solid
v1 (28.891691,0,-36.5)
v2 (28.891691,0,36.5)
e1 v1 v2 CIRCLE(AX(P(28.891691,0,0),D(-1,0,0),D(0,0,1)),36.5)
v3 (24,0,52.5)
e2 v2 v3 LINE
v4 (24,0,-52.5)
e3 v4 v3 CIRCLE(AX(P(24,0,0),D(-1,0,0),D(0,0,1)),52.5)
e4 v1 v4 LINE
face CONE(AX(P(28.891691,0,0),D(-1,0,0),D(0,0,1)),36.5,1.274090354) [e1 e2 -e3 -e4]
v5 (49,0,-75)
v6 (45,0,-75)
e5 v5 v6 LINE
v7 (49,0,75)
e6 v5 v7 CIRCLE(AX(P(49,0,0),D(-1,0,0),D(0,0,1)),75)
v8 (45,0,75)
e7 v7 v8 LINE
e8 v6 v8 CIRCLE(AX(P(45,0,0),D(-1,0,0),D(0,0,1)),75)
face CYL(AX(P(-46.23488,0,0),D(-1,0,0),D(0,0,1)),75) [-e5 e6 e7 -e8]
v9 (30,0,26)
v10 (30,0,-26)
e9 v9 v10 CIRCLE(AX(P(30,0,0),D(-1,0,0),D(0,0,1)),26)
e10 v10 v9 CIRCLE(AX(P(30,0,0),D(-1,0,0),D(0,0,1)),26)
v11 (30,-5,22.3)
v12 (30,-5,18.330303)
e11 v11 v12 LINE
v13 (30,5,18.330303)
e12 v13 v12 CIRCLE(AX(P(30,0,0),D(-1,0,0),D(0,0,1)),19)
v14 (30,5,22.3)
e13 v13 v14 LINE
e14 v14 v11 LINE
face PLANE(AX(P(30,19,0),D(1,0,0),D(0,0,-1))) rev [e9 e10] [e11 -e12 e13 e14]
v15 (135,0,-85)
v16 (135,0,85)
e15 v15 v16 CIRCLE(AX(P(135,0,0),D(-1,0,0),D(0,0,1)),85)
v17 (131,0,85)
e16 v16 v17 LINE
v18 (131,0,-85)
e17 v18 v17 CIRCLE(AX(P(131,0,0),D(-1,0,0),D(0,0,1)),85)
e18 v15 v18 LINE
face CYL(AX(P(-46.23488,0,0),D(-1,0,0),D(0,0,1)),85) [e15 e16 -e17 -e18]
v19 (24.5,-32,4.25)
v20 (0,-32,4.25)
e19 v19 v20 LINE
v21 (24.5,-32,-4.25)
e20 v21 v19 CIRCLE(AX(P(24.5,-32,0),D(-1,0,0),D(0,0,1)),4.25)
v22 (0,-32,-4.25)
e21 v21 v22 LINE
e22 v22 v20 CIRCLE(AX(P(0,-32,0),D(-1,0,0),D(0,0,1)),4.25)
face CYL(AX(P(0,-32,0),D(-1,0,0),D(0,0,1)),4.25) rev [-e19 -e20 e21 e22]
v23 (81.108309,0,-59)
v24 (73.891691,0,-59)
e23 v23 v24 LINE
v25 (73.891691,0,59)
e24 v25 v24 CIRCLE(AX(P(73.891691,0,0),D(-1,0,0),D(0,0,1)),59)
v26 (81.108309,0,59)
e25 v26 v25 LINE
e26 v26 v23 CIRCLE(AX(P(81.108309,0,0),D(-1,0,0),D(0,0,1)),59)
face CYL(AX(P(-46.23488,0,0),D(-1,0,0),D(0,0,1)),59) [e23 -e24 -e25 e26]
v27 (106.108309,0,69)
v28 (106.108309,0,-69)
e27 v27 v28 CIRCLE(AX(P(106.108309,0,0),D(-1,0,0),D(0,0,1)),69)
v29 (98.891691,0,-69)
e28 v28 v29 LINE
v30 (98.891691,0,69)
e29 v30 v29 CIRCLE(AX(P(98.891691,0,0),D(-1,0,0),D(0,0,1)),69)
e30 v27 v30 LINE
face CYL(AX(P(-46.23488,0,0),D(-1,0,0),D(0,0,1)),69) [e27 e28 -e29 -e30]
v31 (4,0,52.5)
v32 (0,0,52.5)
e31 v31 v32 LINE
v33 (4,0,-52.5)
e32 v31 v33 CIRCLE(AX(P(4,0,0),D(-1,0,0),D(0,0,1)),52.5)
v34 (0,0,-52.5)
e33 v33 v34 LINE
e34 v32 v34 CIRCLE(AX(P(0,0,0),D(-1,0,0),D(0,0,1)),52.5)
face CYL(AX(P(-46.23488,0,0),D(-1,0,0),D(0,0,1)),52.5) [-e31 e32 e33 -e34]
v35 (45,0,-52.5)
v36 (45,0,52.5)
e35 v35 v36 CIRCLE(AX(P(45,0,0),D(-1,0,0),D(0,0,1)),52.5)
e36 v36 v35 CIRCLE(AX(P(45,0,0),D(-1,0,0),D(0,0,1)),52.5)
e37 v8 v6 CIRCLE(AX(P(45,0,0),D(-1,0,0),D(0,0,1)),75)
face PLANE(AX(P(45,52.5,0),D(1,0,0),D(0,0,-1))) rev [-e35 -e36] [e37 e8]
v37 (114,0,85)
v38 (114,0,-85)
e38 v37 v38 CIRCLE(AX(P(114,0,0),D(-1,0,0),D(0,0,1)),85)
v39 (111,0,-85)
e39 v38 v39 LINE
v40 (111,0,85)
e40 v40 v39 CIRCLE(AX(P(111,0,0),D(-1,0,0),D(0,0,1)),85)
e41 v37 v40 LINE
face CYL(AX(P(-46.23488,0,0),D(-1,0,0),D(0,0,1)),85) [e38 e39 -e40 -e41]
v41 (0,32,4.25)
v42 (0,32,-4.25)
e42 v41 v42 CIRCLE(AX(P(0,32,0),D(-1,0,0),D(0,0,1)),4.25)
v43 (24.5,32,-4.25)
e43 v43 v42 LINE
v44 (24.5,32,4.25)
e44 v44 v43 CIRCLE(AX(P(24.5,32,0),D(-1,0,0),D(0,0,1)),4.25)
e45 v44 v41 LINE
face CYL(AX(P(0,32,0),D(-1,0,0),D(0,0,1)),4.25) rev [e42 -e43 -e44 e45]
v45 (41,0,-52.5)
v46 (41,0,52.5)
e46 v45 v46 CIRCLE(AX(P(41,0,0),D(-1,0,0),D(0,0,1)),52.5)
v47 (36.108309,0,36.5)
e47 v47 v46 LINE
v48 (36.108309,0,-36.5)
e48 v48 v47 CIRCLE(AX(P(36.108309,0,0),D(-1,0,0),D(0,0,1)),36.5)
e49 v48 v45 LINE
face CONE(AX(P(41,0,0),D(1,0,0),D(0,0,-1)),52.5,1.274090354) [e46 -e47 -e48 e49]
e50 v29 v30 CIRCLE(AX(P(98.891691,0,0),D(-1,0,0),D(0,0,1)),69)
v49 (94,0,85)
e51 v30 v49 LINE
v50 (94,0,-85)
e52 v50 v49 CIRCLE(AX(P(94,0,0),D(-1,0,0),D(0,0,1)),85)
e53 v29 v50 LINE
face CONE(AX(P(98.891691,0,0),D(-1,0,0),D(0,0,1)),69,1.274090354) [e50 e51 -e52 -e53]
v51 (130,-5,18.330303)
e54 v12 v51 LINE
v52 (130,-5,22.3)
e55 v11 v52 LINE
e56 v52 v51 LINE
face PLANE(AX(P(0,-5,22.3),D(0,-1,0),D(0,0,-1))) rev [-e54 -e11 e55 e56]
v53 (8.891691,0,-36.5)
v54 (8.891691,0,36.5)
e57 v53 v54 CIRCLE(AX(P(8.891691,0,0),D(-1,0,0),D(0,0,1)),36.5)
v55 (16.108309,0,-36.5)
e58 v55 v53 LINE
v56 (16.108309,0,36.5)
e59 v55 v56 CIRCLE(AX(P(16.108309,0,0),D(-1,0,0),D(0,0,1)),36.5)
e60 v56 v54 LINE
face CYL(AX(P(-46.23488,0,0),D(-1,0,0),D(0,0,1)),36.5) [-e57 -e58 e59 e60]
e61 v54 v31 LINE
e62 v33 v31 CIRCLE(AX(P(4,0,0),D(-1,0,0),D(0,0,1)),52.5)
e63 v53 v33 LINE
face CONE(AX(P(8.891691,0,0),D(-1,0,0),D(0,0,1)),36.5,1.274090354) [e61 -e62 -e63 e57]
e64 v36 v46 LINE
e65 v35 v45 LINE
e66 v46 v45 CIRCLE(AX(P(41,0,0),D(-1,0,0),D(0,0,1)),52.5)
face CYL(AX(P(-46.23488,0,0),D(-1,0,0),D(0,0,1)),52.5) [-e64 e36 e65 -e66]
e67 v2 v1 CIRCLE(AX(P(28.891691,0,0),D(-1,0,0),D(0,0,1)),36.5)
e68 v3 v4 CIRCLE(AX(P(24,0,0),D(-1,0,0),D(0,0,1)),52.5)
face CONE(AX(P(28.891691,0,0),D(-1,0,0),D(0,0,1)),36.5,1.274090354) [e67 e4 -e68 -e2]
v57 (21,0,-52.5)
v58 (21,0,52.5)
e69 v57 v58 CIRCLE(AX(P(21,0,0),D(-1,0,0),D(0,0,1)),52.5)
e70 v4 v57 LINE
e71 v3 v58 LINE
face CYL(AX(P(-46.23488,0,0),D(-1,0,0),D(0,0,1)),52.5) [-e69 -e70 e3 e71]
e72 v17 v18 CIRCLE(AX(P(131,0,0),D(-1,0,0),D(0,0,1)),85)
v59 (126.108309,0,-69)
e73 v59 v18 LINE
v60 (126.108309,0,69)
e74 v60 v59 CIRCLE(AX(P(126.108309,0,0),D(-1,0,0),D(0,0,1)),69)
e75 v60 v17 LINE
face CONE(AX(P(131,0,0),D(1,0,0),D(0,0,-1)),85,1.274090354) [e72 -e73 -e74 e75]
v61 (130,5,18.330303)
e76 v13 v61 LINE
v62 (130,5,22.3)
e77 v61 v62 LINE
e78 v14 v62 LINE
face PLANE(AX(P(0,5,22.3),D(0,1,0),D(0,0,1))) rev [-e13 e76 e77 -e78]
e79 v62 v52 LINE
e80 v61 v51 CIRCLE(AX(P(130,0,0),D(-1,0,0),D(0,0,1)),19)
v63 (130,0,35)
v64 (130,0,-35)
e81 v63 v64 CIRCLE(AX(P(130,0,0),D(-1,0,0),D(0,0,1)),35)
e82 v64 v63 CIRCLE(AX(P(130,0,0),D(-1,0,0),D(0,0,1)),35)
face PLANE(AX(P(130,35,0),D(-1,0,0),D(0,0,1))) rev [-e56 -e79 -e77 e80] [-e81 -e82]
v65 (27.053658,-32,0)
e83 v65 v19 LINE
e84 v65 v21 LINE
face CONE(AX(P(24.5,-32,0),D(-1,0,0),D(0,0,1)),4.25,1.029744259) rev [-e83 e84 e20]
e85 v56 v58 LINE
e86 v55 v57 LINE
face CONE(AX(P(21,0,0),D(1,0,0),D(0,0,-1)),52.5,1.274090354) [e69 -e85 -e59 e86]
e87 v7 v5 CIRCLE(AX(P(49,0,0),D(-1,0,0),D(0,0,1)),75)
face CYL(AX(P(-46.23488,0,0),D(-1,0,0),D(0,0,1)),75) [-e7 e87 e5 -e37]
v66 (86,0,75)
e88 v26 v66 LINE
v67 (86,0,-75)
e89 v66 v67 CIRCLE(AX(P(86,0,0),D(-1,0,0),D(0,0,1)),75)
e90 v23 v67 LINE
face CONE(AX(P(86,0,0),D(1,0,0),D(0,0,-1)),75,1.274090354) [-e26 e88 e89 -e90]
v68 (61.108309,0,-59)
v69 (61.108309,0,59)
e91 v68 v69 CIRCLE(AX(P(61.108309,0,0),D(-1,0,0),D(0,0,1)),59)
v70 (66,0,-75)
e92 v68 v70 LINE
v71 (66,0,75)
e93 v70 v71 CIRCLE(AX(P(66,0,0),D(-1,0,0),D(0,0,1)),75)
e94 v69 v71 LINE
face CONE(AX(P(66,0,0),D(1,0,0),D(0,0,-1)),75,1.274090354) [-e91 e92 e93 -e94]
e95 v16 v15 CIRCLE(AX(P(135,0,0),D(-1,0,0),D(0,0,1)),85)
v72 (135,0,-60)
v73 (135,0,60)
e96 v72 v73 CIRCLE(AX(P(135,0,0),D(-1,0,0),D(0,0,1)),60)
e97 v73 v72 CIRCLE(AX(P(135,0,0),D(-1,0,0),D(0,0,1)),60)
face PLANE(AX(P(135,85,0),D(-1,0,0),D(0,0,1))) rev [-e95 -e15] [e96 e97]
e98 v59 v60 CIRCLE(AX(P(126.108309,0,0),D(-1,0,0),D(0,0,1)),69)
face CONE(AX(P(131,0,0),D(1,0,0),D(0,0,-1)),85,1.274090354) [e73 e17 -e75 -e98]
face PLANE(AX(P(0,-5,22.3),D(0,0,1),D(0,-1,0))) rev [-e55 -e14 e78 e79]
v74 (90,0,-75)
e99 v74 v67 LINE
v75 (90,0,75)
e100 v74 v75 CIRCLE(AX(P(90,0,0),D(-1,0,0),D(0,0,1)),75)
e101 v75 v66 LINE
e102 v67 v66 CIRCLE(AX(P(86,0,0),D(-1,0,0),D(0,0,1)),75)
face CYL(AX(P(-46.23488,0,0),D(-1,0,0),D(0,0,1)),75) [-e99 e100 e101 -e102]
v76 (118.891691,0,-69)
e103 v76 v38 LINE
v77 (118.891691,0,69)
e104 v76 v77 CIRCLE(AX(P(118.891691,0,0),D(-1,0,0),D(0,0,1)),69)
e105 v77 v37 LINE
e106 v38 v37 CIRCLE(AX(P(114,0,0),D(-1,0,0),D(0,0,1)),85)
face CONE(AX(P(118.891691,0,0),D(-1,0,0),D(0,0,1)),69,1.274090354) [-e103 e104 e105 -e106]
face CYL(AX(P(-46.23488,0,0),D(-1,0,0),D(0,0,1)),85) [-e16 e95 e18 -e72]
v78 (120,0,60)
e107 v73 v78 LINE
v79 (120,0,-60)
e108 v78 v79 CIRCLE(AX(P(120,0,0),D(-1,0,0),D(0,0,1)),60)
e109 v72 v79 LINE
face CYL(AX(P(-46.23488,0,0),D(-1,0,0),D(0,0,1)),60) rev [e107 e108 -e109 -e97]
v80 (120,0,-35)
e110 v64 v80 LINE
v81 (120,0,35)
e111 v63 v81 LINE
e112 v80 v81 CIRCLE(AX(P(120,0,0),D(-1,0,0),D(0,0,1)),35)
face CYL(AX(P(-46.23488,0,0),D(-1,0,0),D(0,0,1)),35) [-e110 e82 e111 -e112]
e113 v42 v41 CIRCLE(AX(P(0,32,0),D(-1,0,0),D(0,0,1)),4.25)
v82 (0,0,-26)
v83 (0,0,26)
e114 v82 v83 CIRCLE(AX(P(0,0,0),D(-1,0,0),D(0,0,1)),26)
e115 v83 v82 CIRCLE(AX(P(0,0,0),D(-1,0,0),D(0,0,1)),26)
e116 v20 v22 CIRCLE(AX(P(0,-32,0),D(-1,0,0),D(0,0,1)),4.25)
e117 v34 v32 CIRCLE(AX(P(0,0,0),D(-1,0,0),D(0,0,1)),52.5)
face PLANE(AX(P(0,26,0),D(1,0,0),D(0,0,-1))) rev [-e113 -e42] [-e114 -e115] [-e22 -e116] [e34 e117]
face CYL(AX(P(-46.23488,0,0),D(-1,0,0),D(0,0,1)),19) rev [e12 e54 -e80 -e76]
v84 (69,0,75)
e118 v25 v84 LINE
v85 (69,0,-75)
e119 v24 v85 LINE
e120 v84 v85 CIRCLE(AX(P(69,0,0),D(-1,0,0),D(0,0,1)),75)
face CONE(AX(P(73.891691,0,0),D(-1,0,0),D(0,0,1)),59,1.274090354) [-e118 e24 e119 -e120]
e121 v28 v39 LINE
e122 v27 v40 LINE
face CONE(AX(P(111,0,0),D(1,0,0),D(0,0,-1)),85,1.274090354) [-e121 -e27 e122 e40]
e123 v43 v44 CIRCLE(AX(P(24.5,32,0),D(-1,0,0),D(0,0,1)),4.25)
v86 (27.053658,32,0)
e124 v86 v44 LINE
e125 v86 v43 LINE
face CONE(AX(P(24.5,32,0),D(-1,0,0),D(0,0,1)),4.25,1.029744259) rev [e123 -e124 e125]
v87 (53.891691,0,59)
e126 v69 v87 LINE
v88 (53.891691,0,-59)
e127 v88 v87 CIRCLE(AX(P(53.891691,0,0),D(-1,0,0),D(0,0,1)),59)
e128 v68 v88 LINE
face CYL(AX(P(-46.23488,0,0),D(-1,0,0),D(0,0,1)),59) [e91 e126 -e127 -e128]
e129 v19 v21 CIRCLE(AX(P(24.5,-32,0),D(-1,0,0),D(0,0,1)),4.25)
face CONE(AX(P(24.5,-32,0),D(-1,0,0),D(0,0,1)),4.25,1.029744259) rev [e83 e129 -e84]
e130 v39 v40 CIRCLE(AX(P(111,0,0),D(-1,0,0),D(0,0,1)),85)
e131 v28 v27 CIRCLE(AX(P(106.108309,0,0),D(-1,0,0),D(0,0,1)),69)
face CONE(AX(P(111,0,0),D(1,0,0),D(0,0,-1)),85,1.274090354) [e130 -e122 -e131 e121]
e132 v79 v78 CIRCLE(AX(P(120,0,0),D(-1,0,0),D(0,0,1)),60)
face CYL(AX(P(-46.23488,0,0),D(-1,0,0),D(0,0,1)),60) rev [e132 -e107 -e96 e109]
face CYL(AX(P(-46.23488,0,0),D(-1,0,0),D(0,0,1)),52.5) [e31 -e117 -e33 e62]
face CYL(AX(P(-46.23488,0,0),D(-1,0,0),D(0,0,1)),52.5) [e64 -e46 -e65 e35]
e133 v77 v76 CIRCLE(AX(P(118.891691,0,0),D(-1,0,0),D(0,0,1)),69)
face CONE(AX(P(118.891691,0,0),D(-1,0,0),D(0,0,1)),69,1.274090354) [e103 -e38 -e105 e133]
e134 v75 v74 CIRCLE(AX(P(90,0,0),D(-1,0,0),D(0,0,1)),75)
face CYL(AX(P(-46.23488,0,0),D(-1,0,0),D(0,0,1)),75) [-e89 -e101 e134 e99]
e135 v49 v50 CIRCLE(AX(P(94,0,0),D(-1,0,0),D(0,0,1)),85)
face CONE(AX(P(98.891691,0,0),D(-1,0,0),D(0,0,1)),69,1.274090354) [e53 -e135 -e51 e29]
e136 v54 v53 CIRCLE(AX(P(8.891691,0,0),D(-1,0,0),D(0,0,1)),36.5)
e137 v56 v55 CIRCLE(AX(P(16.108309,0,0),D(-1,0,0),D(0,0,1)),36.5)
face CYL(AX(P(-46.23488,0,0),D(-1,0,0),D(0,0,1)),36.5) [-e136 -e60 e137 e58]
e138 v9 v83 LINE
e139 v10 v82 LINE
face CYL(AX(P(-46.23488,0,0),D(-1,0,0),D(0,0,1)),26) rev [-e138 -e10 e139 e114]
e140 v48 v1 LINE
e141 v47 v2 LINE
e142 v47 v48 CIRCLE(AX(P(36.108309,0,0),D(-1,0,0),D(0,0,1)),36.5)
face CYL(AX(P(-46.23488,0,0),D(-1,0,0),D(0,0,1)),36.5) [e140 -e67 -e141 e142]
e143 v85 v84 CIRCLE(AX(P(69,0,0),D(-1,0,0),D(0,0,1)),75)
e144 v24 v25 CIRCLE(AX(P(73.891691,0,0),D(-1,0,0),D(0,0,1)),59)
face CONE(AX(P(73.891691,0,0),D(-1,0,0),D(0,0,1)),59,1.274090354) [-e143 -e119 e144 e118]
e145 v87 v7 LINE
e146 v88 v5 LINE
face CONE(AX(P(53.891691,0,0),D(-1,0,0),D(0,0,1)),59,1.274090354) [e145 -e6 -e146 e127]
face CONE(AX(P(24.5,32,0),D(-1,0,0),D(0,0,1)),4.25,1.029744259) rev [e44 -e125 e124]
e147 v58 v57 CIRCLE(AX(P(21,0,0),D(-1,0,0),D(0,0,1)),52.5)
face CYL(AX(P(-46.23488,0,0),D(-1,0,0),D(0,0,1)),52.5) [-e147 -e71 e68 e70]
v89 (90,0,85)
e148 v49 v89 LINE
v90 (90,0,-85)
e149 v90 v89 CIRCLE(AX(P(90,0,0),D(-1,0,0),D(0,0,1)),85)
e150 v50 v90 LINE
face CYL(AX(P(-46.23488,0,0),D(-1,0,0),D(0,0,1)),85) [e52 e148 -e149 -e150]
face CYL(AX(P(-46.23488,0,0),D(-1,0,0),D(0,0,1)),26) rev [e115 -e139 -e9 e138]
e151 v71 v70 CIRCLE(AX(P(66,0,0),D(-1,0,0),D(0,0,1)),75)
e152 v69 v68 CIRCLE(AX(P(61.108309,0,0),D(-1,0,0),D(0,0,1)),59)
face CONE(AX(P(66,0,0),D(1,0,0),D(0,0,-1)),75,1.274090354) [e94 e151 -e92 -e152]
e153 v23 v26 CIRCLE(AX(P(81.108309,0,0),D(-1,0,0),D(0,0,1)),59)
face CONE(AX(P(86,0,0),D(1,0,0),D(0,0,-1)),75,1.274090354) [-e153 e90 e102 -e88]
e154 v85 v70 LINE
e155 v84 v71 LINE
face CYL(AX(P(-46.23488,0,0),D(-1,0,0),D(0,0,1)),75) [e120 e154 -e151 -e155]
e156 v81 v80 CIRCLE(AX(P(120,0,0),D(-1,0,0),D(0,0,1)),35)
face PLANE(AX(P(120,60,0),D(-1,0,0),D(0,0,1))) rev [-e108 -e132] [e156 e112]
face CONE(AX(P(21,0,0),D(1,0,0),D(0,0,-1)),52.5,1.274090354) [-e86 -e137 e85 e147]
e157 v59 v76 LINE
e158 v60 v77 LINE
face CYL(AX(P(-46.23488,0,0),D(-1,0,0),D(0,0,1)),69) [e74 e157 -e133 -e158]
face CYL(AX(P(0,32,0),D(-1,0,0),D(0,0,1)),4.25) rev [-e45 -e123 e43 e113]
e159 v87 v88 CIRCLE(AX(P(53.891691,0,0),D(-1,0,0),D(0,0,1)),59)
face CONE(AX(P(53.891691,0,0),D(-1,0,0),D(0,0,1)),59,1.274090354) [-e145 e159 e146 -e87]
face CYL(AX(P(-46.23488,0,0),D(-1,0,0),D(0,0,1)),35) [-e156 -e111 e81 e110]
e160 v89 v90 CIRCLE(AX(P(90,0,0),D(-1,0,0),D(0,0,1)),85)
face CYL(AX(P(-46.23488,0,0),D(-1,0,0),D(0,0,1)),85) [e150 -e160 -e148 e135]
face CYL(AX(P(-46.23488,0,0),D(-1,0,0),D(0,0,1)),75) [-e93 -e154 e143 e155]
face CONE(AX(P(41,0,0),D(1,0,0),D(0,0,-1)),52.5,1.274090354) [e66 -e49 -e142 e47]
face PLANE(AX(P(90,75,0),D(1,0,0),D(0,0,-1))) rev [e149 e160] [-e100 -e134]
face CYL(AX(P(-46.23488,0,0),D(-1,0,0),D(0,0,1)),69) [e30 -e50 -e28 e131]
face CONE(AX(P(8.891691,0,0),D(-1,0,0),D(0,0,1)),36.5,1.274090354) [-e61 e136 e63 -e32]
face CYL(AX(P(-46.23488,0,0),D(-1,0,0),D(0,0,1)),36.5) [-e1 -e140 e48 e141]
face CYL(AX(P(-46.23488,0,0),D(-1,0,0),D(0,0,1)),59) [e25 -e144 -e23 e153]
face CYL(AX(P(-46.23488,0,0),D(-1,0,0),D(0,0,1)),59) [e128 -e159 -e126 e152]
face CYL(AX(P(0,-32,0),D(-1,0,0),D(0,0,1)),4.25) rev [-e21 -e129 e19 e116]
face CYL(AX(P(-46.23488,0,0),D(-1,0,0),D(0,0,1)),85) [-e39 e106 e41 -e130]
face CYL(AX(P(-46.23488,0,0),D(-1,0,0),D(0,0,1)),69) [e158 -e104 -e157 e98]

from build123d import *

# Parameters (mm, degrees)
HOLE_WIZARD_M10_1_D     = 8.5
HOLE_WIZARD_M10_1_DEPTH = 24.5
HOLE_WIZARD_M10_1_TIP   = 2.553657631
SKETCH_6_W              = 3.96969722
SKETCH_6_H              = 10
CUT_EXTRUDE_1_DEPTH     = 178.059312096


with BuildPart() as part:
    # 草图1 → 旋转1 (revolve)
    with BuildSketch(Plane.XY, mode=Mode.PRIVATE) as revolve_1_sk:
        Polygon((0, 26), (0, 52.5), (4, 52.5), (8.891690903, 36.5), (16.108309097, 36.5), (21, 52.5), (24, 52.5), (28.891690903, 36.5), (36.108309097, 36.5), (41, 52.5), (45, 52.5), (45, 75), (49, 75), (53.891690903, 59), (61.108309097, 59), (66, 75), (69, 75), (73.891690903, 59), (81.108309097, 59), (86, 75), (90, 75), (90, 85), (94, 85), (98.891690903, 69), (106.108309097, 69), (111, 85), (114, 85), (118.891690903, 69), (126.108309097, 69), (131, 85), (135, 85), (135, 60), (120, 60), (120, 35), (130, 35), (130, 19), (30, 19), (30, 26), align=None)
    revolve(revolve_1_sk.sketch.rotate(Axis((-46.234880066, 0, 0), (1, 0, 0)), 90), axis=Axis((-46.234880066, 0, 0), (1, 0, 0)))

    # M10 螺纹孔1
    with Locations(Plane.ZY):
        with Locations((0, 32), (0, -32)):
            Hole(HOLE_WIZARD_M10_1_D / 2, depth=HOLE_WIZARD_M10_1_DEPTH)
            with Locations((0, 0, -(HOLE_WIZARD_M10_1_DEPTH + HOLE_WIZARD_M10_1_TIP / 2))):  # 118° drill point
                Cone(0, HOLE_WIZARD_M10_1_D / 2, HOLE_WIZARD_M10_1_TIP, mode=Mode.SUBTRACT)

    # 草图6 → 切除-拉伸1 (cut, through all)
    with BuildSketch(Plane(origin=(130, 0, 0), x_dir=(0, 0, -1), z_dir=(1, 0, 0))):
        with Locations((-20.31515139, 0)):
            Rectangle(SKETCH_6_W, SKETCH_6_H)
    extrude(amount=-CUT_EXTRUDE_1_DEPTH, mode=Mode.SUBTRACT)


solid = part.part
